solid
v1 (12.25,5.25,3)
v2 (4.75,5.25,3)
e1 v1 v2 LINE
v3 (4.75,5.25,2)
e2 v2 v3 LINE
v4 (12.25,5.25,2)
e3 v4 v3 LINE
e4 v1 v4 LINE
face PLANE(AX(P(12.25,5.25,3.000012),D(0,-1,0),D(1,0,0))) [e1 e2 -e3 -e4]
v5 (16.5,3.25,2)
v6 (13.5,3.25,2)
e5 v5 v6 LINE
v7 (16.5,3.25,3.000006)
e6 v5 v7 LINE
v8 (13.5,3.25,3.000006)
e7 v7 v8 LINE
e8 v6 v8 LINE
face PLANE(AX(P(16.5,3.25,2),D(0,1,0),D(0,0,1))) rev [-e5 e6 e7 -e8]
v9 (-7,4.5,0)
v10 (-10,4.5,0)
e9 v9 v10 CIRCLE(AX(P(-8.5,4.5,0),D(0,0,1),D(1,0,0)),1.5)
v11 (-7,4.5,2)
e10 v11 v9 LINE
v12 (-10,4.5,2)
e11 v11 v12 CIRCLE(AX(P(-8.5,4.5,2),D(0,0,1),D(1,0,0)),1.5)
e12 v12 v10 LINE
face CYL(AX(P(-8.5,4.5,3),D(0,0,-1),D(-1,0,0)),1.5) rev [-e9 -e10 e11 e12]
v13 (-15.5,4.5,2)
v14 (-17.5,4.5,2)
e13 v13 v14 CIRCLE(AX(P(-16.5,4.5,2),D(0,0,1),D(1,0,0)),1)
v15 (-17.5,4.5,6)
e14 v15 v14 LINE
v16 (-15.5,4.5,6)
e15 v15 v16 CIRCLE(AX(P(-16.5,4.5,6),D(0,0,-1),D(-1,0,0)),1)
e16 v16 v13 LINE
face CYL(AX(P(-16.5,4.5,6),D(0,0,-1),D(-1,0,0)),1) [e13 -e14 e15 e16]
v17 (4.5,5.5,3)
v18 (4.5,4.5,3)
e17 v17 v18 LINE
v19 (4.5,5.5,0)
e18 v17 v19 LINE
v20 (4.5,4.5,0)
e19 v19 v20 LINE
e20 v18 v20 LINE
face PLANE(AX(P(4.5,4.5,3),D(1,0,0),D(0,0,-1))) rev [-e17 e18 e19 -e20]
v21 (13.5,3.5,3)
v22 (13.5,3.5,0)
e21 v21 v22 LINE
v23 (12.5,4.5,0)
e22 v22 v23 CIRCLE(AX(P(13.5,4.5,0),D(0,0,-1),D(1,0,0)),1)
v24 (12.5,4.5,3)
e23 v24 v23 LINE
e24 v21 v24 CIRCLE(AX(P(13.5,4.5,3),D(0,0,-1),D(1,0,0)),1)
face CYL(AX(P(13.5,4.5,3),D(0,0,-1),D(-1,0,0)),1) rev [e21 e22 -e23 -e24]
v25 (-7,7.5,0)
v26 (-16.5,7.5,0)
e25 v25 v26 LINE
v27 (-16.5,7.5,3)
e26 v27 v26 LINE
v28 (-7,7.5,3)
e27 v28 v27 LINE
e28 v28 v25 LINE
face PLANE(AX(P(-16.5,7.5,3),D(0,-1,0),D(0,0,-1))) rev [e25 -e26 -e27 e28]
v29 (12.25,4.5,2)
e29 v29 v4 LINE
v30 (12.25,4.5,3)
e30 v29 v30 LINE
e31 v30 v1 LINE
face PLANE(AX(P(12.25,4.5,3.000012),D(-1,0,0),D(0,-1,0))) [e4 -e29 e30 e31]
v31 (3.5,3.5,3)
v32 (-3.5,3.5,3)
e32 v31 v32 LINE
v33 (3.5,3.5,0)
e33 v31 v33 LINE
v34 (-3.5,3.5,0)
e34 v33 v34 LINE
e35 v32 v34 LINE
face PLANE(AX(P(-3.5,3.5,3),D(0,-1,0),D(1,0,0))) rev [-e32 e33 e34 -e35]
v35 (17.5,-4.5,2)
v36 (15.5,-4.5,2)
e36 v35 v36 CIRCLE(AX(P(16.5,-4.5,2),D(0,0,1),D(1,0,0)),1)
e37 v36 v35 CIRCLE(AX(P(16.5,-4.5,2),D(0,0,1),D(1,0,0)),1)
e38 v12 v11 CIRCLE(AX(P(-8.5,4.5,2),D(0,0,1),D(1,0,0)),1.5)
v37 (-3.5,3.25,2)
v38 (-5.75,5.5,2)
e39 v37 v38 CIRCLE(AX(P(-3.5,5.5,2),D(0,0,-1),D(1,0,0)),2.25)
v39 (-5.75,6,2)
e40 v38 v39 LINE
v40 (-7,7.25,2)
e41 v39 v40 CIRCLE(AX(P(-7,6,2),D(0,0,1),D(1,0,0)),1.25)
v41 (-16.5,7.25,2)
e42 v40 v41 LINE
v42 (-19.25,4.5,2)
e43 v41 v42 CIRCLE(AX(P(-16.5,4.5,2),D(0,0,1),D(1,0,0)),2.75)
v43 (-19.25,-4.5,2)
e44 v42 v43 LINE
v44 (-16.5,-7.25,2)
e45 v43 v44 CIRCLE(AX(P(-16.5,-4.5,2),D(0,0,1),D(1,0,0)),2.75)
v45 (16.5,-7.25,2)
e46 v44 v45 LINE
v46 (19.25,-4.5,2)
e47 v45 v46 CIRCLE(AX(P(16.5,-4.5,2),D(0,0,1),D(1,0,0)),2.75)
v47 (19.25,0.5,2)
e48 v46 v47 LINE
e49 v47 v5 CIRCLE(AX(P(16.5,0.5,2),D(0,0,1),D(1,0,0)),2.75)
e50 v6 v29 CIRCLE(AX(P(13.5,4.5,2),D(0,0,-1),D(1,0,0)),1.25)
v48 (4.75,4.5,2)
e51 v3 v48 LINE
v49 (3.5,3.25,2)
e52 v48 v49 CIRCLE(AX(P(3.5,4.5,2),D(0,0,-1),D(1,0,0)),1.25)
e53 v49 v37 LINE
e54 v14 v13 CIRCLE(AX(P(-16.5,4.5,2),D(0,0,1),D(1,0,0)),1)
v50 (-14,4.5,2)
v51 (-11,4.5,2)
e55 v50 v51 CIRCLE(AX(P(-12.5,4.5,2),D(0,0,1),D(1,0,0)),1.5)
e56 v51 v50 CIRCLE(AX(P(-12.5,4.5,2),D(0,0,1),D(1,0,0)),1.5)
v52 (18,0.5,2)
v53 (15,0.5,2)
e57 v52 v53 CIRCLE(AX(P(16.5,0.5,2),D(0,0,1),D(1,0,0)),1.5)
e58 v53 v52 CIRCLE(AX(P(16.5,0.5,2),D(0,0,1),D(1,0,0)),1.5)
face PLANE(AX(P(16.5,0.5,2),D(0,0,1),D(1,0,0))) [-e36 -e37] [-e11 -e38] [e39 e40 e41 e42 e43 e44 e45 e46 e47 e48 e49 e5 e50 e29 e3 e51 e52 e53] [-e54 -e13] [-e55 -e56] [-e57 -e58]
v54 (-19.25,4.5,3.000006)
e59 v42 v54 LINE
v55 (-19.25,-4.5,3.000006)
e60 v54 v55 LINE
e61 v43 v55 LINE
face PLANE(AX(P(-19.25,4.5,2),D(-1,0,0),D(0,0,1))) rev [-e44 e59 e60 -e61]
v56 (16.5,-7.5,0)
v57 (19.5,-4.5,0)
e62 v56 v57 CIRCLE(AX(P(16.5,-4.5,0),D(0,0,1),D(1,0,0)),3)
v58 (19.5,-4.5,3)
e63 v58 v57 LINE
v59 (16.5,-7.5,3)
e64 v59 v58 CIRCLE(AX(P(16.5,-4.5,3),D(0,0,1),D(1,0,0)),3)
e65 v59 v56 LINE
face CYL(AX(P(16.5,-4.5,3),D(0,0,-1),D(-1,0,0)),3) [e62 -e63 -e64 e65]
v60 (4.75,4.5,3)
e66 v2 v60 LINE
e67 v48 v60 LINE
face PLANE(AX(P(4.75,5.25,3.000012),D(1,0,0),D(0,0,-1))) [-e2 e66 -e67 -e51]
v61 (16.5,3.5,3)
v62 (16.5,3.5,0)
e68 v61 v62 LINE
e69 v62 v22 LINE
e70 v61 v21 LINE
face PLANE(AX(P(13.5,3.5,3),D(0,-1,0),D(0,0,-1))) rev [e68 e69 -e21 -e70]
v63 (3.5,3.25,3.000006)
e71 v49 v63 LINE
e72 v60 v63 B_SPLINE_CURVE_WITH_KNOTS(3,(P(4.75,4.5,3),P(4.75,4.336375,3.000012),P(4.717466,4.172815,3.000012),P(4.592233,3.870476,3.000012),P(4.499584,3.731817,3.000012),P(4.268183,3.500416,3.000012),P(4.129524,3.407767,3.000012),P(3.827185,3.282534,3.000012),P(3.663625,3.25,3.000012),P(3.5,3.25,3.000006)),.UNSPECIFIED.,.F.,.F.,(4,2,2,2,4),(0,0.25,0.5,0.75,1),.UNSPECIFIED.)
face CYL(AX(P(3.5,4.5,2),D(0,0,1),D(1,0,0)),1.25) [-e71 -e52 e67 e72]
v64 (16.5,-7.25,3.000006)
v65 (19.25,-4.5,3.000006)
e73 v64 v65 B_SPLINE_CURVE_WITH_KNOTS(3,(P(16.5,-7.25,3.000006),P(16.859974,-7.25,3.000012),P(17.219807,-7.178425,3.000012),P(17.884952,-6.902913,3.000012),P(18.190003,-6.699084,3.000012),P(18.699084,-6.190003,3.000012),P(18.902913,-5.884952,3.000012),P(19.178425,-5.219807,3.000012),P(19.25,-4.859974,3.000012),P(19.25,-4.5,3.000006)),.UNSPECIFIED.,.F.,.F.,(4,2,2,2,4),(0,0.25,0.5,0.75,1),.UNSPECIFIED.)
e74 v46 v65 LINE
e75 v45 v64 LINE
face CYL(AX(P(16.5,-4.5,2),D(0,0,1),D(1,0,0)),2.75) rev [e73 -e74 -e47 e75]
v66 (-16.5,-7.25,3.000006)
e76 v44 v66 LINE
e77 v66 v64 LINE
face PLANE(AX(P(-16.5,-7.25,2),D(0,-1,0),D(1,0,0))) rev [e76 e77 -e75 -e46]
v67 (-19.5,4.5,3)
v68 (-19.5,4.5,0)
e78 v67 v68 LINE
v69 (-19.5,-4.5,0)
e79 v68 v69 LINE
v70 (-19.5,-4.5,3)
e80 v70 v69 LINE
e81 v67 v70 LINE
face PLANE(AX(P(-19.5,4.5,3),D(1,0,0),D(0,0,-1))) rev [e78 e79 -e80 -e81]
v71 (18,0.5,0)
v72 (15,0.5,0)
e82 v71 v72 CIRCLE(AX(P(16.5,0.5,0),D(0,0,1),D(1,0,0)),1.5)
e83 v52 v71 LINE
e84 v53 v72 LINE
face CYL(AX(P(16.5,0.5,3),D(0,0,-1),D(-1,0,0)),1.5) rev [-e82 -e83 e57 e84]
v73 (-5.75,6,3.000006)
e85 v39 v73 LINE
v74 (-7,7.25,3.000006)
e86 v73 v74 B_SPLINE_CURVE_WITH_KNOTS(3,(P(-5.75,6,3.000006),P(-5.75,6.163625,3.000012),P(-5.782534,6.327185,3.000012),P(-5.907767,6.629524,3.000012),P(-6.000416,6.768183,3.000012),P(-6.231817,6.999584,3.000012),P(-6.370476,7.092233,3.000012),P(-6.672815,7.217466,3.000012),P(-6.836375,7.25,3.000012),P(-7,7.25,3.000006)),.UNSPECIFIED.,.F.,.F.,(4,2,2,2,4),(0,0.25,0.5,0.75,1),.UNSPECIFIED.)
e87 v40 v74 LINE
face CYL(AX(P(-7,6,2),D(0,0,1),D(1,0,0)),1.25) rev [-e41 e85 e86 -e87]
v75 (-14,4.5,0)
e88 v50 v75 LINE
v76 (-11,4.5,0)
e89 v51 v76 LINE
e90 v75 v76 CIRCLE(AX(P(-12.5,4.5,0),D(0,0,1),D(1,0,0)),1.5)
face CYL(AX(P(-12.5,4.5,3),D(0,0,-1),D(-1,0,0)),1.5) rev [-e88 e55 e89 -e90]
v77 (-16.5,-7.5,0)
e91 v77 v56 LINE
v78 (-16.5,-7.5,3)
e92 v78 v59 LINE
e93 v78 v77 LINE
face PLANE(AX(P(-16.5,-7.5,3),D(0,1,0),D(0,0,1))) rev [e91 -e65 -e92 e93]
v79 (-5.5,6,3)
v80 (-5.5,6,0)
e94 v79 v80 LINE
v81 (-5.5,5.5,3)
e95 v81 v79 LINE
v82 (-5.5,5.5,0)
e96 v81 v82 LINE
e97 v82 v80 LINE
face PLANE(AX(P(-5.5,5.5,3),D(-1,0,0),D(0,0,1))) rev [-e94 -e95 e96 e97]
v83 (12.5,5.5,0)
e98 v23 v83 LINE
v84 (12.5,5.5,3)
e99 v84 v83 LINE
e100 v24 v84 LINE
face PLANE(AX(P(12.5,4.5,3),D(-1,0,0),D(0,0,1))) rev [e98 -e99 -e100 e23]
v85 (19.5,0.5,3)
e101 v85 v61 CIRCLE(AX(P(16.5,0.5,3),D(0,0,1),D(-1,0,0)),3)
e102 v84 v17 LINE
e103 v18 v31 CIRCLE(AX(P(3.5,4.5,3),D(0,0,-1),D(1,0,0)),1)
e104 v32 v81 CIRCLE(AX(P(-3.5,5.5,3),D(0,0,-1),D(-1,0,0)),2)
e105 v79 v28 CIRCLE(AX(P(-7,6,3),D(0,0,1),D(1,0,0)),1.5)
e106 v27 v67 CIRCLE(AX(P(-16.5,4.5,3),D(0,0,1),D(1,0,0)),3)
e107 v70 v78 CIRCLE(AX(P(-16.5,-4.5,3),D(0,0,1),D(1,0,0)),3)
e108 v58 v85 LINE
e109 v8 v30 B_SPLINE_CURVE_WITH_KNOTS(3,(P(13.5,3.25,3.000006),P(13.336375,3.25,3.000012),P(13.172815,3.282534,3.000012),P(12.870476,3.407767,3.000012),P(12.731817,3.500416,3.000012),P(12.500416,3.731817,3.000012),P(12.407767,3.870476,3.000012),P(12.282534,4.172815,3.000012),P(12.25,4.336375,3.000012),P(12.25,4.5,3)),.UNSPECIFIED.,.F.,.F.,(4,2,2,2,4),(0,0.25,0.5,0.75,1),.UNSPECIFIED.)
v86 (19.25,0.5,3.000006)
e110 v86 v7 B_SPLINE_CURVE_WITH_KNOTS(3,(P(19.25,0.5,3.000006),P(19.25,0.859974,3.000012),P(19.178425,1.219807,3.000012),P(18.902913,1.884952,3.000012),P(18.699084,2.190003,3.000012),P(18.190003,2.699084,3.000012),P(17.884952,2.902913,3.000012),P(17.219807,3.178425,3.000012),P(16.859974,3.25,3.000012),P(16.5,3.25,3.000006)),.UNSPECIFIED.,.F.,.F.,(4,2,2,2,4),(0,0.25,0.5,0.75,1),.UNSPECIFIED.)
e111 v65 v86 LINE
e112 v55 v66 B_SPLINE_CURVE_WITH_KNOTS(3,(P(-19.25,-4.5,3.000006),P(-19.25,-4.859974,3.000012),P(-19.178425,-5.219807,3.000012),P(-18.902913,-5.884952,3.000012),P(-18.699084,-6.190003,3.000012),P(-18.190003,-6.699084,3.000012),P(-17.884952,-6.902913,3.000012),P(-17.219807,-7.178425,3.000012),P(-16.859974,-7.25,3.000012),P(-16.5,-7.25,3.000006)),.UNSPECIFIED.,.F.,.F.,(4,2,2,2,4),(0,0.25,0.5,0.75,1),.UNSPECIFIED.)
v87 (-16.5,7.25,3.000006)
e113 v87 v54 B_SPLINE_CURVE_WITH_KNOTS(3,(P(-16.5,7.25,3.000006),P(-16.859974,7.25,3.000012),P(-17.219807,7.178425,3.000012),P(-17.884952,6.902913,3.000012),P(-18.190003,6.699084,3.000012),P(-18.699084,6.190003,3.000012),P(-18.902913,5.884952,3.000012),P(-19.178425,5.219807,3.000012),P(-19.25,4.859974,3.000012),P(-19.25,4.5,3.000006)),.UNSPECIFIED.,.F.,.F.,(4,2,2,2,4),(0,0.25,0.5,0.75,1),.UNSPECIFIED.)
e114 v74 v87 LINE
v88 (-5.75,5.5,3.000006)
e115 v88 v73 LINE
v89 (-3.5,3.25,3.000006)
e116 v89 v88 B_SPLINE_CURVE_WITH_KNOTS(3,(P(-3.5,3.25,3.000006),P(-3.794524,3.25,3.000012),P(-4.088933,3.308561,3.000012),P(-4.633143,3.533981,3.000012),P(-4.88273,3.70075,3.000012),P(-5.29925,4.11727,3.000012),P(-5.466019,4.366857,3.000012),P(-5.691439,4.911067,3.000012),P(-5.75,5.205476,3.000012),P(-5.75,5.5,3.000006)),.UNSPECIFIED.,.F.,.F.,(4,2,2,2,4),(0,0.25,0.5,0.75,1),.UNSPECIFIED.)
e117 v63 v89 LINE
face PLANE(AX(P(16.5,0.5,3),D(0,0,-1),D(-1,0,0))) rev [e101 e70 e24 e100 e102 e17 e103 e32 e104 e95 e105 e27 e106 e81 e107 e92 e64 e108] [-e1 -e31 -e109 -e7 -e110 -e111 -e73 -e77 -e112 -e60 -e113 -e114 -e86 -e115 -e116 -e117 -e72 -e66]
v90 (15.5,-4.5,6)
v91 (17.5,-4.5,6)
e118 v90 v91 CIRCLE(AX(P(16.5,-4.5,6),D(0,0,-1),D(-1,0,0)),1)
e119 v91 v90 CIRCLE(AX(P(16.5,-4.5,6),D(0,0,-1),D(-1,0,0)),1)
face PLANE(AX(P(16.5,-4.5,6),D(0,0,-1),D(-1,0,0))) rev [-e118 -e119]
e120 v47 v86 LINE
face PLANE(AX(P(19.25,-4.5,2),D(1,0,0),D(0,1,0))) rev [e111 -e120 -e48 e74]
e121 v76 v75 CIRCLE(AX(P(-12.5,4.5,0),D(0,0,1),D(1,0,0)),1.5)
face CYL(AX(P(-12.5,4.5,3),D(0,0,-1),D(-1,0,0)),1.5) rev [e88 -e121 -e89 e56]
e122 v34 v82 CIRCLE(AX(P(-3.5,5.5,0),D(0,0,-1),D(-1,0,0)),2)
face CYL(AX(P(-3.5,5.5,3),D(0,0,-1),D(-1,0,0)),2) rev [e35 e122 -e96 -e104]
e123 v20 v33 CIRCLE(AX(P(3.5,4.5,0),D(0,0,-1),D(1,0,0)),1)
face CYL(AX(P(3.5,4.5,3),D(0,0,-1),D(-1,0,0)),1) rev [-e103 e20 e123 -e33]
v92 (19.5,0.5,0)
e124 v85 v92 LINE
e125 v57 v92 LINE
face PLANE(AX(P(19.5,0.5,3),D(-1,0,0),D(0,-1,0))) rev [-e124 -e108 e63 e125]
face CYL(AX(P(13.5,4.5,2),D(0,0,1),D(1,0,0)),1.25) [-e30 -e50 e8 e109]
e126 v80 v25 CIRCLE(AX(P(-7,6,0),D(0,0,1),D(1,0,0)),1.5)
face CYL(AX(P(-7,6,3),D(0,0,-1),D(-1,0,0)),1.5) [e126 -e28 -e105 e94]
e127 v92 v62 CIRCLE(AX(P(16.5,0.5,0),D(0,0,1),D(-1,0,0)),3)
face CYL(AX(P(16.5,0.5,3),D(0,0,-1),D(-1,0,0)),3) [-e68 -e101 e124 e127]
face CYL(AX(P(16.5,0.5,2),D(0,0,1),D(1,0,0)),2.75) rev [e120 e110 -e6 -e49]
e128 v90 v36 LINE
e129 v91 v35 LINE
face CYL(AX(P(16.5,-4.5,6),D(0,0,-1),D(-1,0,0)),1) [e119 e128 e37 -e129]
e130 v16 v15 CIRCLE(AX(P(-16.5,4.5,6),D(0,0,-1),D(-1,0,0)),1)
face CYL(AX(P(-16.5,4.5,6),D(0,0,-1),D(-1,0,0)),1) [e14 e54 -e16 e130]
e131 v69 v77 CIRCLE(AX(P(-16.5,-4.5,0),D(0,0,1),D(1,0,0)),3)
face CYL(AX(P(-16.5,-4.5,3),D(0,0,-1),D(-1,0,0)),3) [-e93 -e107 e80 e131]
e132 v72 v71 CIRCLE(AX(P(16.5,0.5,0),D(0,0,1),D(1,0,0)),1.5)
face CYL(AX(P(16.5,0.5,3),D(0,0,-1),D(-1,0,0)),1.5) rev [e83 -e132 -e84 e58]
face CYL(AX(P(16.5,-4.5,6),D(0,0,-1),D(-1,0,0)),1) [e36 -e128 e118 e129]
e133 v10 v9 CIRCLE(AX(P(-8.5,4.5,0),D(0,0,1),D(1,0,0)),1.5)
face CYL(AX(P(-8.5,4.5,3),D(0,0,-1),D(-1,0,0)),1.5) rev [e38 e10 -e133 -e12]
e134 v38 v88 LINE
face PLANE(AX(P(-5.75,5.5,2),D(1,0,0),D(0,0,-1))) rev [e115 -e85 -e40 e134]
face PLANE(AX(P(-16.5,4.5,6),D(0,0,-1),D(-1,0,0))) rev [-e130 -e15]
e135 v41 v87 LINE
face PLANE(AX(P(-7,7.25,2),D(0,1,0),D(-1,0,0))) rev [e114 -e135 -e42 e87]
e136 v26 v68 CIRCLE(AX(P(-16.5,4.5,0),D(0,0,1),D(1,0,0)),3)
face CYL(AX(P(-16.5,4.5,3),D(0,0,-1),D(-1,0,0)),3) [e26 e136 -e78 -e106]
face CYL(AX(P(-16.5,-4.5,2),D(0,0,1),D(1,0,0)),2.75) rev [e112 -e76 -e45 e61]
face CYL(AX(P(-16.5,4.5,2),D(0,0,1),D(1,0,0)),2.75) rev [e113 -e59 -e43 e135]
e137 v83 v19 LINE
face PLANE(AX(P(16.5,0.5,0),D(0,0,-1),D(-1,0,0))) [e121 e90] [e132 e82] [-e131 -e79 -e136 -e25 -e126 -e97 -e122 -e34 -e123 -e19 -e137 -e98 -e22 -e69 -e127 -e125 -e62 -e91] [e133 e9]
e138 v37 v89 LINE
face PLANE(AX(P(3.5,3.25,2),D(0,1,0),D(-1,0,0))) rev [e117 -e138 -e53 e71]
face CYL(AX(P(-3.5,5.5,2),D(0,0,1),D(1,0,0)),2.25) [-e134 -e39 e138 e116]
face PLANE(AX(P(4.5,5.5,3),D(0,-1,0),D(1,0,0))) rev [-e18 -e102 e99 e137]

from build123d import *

# Parameters (mm, degrees)
PLATE_OUTLINE_SKETCH_R       = 1
PLATE_OUTLINE_SKETCH_R_2     = 1.5
BASE_PLATE_3MM_DEPTH         = 3
RECESS_POCKET_1MM_DEPTH      = 22.106870919
RECESS_POCKET_1MM_DEPTH_BACK = 1
LOCATING_PIN_SKETCH_R        = 1
LOCATING_PINS_2X_DEPTH       = 6


with BuildPart() as part:
    # Plate Outline Sketch → Base Plate 3mm (new body)
    with BuildSketch(Plane.XY):
        with BuildLine():
            Line((4.5, 5.5), (12.5, 5.5))
            Line((12.5, 5.5), (12.5, 4.5))
            ThreePointArc((12.5, 4.5), (12.792893219, 3.792893219), (13.5, 3.5))
            Line((13.5, 3.5), (16.5, 3.5))
            ThreePointArc((16.5, 3.5), (18.621320344, 2.621320344), (19.5, 0.5))
            Line((19.5, 0.5), (19.5, -4.5))
            ThreePointArc((19.5, -4.5), (18.621320344, -6.621320344), (16.5, -7.5))
            Line((16.5, -7.5), (-16.5, -7.5))
            ThreePointArc((-16.5, -7.5), (-18.621320344, -6.621320344), (-19.5, -4.5))
            Line((-19.5, -4.5), (-19.5, 4.5))
            ThreePointArc((-19.5, 4.5), (-18.621320344, 6.621320344), (-16.5, 7.5))
            Line((-16.5, 7.5), (-7, 7.5))
            ThreePointArc((-7, 7.5), (-5.939339828, 7.060660172), (-5.5, 6))
            Line((-5.5, 6), (-5.5, 5.5))
            ThreePointArc((-5.5, 5.5), (-4.914213562, 4.085786438), (-3.5, 3.5))
            Line((-3.5, 3.5), (3.5, 3.5))
            ThreePointArc((3.5, 3.5), (4.207106781, 3.792893219), (4.5, 4.5))
            Line((4.5, 4.5), (4.5, 5.5))
        make_face()
        with Locations((-16.5, 4.5)):
            Circle(PLATE_OUTLINE_SKETCH_R, mode=Mode.SUBTRACT)
        with Locations((-12.5, 4.5)):
            Circle(PLATE_OUTLINE_SKETCH_R_2, mode=Mode.SUBTRACT)
        with Locations((-8.5, 4.5)):
            Circle(PLATE_OUTLINE_SKETCH_R_2, mode=Mode.SUBTRACT)
        with Locations((16.5, 0.5)):
            Circle(PLATE_OUTLINE_SKETCH_R_2, mode=Mode.SUBTRACT)
        with Locations((16.5, -4.5)):
            Circle(PLATE_OUTLINE_SKETCH_R, mode=Mode.SUBTRACT)
    extrude(amount=BASE_PLATE_3MM_DEPTH)

    # Pocket Outline Sketch → Recess Pocket 1mm (cut, two sides: drawn at the far end of the back side and taken through both)
    with BuildSketch(Plane.XY.offset(3).offset(-RECESS_POCKET_1MM_DEPTH_BACK)):
        with BuildLine():
            Line((16.5, 3.25), (13.5, 3.25))
            ThreePointArc((13.5, 3.25), (12.616116524, 3.616116524), (12.25, 4.5))
            Line((12.25, 4.5), (12.25, 5.25))
            Line((12.25, 5.25), (4.75, 5.25))
            Line((4.75, 5.25), (4.75, 4.5))
            ThreePointArc((4.75, 4.5), (4.383883476, 3.616116524), (3.5, 3.25))
            Line((3.5, 3.25), (-3.5, 3.25))
            ThreePointArc((-3.5, 3.25), (-5.090990258, 3.909009742), (-5.75, 5.5))
            Line((-5.75, 5.5), (-5.75, 6))
            ThreePointArc((-5.75, 6), (-6.116116524, 6.883883476), (-7, 7.25))
            Line((-7, 7.25), (-16.5, 7.25))
            ThreePointArc((-16.5, 7.25), (-18.444543648, 6.444543648), (-19.25, 4.5))
            Line((-19.25, 4.5), (-19.25, -4.5))
            ThreePointArc((-19.25, -4.5), (-18.444543648, -6.444543648), (-16.5, -7.25))
            Line((-16.5, -7.25), (16.5, -7.25))
            ThreePointArc((16.5, -7.25), (18.444543648, -6.444543648), (19.25, -4.5))
            Line((19.25, -4.5), (19.25, 0.5))
            ThreePointArc((19.25, 0.5), (18.444543648, 2.444543648), (16.5, 3.25))
        make_face()
    extrude(amount=RECESS_POCKET_1MM_DEPTH + RECESS_POCKET_1MM_DEPTH_BACK, mode=Mode.SUBTRACT)

    # Locating Pin Sketch → Locating Pins 2x (add)
    with BuildSketch(Plane(origin=(0, 0, 0), x_dir=(-1, 0, 0), z_dir=(0, 0, -1))):
        with Locations((16.5, 4.5)):
            Circle(LOCATING_PIN_SKETCH_R)
        with Locations((-16.5, -4.5)):
            Circle(LOCATING_PIN_SKETCH_R)
    extrude(amount=-LOCATING_PINS_2X_DEPTH)


solid = part.part
